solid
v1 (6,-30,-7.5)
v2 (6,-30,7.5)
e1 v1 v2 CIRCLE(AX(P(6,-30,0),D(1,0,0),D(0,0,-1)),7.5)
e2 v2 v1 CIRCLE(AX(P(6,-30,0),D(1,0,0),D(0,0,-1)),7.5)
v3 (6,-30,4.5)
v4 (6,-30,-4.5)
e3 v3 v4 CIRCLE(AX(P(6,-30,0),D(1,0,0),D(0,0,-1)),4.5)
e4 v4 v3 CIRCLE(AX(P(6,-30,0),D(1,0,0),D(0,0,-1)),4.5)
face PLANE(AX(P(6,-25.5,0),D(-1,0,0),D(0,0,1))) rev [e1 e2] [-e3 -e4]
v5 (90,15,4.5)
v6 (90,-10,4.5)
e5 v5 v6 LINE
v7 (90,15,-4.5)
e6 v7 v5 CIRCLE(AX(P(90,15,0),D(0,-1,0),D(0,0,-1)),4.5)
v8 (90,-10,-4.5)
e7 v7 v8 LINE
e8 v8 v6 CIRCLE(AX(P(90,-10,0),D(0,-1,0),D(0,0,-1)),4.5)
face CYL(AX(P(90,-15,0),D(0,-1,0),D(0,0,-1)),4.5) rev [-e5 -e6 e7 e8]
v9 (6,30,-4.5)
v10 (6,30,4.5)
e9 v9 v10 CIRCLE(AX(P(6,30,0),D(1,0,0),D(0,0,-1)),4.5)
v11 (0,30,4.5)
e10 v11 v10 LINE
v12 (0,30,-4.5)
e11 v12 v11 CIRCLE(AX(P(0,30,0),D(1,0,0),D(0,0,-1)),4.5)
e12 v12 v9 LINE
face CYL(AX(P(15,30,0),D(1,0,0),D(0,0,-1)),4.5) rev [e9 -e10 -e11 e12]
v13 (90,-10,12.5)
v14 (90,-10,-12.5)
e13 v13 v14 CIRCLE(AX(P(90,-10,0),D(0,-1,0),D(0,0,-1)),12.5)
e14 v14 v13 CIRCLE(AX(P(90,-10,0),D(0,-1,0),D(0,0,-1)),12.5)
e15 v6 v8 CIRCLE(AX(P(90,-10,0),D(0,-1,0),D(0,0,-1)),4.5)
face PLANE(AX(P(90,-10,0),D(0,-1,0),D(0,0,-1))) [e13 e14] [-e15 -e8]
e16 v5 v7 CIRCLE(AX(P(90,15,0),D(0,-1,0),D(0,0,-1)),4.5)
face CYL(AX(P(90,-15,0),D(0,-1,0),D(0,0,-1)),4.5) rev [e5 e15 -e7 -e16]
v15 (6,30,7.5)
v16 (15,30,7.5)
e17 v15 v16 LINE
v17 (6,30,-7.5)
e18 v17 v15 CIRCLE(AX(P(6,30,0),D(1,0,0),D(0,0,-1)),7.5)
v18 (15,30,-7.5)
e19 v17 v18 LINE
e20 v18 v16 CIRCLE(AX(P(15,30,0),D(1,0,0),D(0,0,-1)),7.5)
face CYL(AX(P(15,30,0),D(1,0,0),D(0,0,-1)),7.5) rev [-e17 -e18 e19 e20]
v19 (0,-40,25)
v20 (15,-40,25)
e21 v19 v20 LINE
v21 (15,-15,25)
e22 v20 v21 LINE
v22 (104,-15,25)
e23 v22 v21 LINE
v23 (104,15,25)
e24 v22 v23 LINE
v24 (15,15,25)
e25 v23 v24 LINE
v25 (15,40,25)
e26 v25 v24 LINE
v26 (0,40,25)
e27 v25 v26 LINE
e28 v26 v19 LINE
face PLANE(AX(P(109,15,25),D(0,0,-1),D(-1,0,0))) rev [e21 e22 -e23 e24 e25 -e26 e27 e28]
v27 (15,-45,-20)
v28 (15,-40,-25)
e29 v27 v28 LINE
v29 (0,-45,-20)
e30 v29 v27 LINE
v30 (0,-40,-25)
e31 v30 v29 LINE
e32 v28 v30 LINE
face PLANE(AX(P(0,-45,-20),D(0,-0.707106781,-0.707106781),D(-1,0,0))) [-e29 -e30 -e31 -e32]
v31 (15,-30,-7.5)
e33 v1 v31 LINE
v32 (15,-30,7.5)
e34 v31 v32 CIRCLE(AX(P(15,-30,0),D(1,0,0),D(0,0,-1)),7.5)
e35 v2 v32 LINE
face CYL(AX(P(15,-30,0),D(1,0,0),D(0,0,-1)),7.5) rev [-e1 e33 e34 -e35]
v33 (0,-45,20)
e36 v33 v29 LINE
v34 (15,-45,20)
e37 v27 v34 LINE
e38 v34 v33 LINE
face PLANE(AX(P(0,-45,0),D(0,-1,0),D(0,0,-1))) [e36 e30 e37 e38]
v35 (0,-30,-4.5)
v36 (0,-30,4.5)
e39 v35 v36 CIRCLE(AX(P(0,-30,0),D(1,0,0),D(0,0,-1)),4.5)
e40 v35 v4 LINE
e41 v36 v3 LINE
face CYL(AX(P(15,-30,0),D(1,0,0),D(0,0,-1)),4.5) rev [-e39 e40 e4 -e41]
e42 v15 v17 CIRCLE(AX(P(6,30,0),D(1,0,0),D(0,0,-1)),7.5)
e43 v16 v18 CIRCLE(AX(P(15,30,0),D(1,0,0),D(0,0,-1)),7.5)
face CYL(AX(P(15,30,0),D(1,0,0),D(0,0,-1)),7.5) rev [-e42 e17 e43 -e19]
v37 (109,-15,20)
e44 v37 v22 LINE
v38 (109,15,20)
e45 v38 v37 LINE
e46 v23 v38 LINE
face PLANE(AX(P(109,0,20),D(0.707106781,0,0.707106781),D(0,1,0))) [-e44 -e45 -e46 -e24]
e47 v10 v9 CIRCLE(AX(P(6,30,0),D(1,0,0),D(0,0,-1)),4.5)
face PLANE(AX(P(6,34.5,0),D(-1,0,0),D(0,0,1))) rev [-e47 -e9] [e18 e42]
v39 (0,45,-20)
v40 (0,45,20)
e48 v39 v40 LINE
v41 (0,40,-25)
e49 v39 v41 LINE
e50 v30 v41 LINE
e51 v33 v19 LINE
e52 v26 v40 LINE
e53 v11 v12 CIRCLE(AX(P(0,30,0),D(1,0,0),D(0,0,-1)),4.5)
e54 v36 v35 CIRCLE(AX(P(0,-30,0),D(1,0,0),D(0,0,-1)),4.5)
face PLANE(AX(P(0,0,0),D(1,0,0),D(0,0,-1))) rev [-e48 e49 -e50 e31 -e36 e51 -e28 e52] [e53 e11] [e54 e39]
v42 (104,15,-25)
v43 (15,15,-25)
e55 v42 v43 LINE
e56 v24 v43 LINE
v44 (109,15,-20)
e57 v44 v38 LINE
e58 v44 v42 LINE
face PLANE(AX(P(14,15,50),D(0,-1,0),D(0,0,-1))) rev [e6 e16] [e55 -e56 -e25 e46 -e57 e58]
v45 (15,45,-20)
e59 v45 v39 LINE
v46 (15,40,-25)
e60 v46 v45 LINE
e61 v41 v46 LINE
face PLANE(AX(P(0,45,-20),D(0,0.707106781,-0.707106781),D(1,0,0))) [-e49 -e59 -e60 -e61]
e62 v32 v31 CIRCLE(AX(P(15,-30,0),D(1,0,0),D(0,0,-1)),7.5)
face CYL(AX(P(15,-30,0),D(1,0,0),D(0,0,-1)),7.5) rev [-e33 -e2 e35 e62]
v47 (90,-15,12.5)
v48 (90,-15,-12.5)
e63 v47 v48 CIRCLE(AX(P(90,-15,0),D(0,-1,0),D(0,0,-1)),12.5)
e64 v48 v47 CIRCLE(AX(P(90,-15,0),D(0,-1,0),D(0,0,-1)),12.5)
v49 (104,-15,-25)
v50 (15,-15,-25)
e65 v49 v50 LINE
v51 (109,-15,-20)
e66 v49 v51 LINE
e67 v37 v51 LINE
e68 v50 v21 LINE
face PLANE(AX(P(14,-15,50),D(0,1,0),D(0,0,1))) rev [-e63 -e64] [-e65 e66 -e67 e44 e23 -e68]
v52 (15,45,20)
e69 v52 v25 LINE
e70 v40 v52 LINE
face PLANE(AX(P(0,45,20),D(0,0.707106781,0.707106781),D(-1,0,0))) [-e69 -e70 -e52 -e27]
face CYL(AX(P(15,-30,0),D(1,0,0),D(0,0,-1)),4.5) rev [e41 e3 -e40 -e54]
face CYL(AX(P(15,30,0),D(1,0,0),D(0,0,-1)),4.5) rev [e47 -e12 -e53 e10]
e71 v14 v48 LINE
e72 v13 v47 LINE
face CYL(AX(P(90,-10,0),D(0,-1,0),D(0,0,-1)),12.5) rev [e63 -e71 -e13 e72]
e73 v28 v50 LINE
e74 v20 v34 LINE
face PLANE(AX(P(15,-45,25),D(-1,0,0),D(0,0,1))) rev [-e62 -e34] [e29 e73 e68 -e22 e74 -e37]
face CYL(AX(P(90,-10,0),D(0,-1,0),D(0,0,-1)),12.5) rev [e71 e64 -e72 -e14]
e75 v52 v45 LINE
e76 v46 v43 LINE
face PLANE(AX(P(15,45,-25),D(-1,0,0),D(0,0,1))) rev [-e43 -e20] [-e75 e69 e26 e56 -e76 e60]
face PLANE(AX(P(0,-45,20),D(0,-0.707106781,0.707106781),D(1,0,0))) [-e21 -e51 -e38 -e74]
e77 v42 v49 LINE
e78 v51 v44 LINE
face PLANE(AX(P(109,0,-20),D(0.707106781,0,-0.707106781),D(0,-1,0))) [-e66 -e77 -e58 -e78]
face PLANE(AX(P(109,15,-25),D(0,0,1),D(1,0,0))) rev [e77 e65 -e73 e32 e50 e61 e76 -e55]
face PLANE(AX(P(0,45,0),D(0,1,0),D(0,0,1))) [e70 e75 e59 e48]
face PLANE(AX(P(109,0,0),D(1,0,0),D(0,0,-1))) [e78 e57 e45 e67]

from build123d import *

# Parameters (mm, degrees)
SKETCH_1_W                = 100
SKETCH_1_H                = 30
EXTRUDE_1_DEPTH           = 14
SKETCH_2_W                = 50
SKETCH_2_H                = 30
EXTRUDE_2_DEPTH           = 95
SKETCH_3_R                = 12.5
CUT_EXTRUDE_1_DEPTH       = 5
HOLE_WIZARD_9_0_9_1_D     = 9
HOLE_WIZARD_9_0_9_2_D     = 9
SKETCH_8_OUTSIDE_W        = 132.186
SKETCH_8_OUTSIDE_H        = 62.186
SKETCH_8_OUTSIDE_W_2      = 50
SKETCH_8_OUTSIDE_H_2      = 30
CUT_EXTRUDE_2_DEPTH       = 121.855285362
SKETCH_9_W                = 15
SKETCH_9_H                = 50
EXTRUDE_3_DEPTH           = 30
SKETCH_10_W               = 15
SKETCH_10_H               = 50
EXTRUDE_4_DEPTH           = 30
HOLE_WIZARD_1_D           = 9
HOLE_WIZARD_1_CBORE_D     = 15
HOLE_WIZARD_1_CBORE_DEPTH = 9
CHAMFER_1_SIZE            = 5


with BuildPart() as part:
    # 草图1 → 凸台-拉伸1 (new body)
    with BuildSketch(Plane(origin=(0, 0, 0), x_dir=(0, 0, -1), z_dir=(1, 0, 0))):
        Rectangle(SKETCH_1_W, SKETCH_1_H)
    extrude(amount=EXTRUDE_1_DEPTH)

    # 草图2 → 凸台-拉伸2 (add)
    with BuildSketch(Plane(origin=(14, 0, 0), x_dir=(0, 0, -1), z_dir=(1, 0, 0))):
        Rectangle(SKETCH_2_W, SKETCH_2_H)
    extrude(amount=EXTRUDE_2_DEPTH)

    # 草图3 → 切除-拉伸1 (cut)
    with BuildSketch(Plane.XZ.offset(15)):
        with Locations(Location((90, 0, 0), (0, 0, 270))):
            Circle(SKETCH_3_R)
    extrude(amount=-CUT_EXTRUDE_1_DEPTH, mode=Mode.SUBTRACT)

    # Ø9.0 (9) 直径孔1 (through all)
    with Locations(Plane(origin=(0, -15, 0), x_dir=(-1, 0, 0), z_dir=(0, -1, 0))):
        with Locations((-90, 0)):
            Hole(HOLE_WIZARD_9_0_9_1_D / 2)

    # Ø9.0 (9) 直径孔2 (through all)
    with Locations(Plane(origin=(14, 0, 0), x_dir=(0, 0, -1), z_dir=(1, 0, 0))):
        with Locations((-40, 0), (40, 0)):
            Hole(HOLE_WIZARD_9_0_9_2_D / 2)

    # 草图8 outside → 切除-拉伸2 (cut, through all)
    with BuildSketch(Plane(origin=(109, 0, 0), x_dir=(0, 0, -1), z_dir=(1, 0, 0))):
        Rectangle(SKETCH_8_OUTSIDE_W, SKETCH_8_OUTSIDE_H)
        Rectangle(SKETCH_8_OUTSIDE_W_2, SKETCH_8_OUTSIDE_H_2, mode=Mode.SUBTRACT)
    extrude(amount=-CUT_EXTRUDE_2_DEPTH, mode=Mode.SUBTRACT)

    # 草图9 → 凸台-拉伸3 (add)
    with BuildSketch(Plane.XZ.offset(15)):
        with Locations((7.5, 0)):
            Rectangle(SKETCH_9_W, SKETCH_9_H)
    extrude(amount=EXTRUDE_3_DEPTH)

    # 草图10 → 凸台-拉伸4 (add)
    with BuildSketch(Plane(origin=(0, 15, 0), x_dir=(1, 0, 0), z_dir=(0, 1, 0))):
        with Locations((7.5, 0)):
            Rectangle(SKETCH_10_W, SKETCH_10_H)
    extrude(amount=EXTRUDE_4_DEPTH)

    # 打孔尺寸(%根据)内六角圆柱头螺钉的类型1 (through all)
    with Locations(Plane(origin=(15, 0, 0), x_dir=(0, 0, -1), z_dir=(1, 0, 0))):
        with Locations((0, 30), (0, -30)):
            CounterBoreHole(HOLE_WIZARD_1_D / 2, HOLE_WIZARD_1_CBORE_D / 2, HOLE_WIZARD_1_CBORE_DEPTH)

    # 倒角1
    chamfer_1_edges = [part.edges().sort_by_distance(p)[0] for p in [
        (109, 0, -25),
        (109, 0, 25),
        (7.5, -45, -25),
        (7.5, -45, 25),
        (7.5, 45, 25),
        (7.5, 45, -25),
    ]]
    chamfer(chamfer_1_edges, length=CHAMFER_1_SIZE)


solid = part.part
